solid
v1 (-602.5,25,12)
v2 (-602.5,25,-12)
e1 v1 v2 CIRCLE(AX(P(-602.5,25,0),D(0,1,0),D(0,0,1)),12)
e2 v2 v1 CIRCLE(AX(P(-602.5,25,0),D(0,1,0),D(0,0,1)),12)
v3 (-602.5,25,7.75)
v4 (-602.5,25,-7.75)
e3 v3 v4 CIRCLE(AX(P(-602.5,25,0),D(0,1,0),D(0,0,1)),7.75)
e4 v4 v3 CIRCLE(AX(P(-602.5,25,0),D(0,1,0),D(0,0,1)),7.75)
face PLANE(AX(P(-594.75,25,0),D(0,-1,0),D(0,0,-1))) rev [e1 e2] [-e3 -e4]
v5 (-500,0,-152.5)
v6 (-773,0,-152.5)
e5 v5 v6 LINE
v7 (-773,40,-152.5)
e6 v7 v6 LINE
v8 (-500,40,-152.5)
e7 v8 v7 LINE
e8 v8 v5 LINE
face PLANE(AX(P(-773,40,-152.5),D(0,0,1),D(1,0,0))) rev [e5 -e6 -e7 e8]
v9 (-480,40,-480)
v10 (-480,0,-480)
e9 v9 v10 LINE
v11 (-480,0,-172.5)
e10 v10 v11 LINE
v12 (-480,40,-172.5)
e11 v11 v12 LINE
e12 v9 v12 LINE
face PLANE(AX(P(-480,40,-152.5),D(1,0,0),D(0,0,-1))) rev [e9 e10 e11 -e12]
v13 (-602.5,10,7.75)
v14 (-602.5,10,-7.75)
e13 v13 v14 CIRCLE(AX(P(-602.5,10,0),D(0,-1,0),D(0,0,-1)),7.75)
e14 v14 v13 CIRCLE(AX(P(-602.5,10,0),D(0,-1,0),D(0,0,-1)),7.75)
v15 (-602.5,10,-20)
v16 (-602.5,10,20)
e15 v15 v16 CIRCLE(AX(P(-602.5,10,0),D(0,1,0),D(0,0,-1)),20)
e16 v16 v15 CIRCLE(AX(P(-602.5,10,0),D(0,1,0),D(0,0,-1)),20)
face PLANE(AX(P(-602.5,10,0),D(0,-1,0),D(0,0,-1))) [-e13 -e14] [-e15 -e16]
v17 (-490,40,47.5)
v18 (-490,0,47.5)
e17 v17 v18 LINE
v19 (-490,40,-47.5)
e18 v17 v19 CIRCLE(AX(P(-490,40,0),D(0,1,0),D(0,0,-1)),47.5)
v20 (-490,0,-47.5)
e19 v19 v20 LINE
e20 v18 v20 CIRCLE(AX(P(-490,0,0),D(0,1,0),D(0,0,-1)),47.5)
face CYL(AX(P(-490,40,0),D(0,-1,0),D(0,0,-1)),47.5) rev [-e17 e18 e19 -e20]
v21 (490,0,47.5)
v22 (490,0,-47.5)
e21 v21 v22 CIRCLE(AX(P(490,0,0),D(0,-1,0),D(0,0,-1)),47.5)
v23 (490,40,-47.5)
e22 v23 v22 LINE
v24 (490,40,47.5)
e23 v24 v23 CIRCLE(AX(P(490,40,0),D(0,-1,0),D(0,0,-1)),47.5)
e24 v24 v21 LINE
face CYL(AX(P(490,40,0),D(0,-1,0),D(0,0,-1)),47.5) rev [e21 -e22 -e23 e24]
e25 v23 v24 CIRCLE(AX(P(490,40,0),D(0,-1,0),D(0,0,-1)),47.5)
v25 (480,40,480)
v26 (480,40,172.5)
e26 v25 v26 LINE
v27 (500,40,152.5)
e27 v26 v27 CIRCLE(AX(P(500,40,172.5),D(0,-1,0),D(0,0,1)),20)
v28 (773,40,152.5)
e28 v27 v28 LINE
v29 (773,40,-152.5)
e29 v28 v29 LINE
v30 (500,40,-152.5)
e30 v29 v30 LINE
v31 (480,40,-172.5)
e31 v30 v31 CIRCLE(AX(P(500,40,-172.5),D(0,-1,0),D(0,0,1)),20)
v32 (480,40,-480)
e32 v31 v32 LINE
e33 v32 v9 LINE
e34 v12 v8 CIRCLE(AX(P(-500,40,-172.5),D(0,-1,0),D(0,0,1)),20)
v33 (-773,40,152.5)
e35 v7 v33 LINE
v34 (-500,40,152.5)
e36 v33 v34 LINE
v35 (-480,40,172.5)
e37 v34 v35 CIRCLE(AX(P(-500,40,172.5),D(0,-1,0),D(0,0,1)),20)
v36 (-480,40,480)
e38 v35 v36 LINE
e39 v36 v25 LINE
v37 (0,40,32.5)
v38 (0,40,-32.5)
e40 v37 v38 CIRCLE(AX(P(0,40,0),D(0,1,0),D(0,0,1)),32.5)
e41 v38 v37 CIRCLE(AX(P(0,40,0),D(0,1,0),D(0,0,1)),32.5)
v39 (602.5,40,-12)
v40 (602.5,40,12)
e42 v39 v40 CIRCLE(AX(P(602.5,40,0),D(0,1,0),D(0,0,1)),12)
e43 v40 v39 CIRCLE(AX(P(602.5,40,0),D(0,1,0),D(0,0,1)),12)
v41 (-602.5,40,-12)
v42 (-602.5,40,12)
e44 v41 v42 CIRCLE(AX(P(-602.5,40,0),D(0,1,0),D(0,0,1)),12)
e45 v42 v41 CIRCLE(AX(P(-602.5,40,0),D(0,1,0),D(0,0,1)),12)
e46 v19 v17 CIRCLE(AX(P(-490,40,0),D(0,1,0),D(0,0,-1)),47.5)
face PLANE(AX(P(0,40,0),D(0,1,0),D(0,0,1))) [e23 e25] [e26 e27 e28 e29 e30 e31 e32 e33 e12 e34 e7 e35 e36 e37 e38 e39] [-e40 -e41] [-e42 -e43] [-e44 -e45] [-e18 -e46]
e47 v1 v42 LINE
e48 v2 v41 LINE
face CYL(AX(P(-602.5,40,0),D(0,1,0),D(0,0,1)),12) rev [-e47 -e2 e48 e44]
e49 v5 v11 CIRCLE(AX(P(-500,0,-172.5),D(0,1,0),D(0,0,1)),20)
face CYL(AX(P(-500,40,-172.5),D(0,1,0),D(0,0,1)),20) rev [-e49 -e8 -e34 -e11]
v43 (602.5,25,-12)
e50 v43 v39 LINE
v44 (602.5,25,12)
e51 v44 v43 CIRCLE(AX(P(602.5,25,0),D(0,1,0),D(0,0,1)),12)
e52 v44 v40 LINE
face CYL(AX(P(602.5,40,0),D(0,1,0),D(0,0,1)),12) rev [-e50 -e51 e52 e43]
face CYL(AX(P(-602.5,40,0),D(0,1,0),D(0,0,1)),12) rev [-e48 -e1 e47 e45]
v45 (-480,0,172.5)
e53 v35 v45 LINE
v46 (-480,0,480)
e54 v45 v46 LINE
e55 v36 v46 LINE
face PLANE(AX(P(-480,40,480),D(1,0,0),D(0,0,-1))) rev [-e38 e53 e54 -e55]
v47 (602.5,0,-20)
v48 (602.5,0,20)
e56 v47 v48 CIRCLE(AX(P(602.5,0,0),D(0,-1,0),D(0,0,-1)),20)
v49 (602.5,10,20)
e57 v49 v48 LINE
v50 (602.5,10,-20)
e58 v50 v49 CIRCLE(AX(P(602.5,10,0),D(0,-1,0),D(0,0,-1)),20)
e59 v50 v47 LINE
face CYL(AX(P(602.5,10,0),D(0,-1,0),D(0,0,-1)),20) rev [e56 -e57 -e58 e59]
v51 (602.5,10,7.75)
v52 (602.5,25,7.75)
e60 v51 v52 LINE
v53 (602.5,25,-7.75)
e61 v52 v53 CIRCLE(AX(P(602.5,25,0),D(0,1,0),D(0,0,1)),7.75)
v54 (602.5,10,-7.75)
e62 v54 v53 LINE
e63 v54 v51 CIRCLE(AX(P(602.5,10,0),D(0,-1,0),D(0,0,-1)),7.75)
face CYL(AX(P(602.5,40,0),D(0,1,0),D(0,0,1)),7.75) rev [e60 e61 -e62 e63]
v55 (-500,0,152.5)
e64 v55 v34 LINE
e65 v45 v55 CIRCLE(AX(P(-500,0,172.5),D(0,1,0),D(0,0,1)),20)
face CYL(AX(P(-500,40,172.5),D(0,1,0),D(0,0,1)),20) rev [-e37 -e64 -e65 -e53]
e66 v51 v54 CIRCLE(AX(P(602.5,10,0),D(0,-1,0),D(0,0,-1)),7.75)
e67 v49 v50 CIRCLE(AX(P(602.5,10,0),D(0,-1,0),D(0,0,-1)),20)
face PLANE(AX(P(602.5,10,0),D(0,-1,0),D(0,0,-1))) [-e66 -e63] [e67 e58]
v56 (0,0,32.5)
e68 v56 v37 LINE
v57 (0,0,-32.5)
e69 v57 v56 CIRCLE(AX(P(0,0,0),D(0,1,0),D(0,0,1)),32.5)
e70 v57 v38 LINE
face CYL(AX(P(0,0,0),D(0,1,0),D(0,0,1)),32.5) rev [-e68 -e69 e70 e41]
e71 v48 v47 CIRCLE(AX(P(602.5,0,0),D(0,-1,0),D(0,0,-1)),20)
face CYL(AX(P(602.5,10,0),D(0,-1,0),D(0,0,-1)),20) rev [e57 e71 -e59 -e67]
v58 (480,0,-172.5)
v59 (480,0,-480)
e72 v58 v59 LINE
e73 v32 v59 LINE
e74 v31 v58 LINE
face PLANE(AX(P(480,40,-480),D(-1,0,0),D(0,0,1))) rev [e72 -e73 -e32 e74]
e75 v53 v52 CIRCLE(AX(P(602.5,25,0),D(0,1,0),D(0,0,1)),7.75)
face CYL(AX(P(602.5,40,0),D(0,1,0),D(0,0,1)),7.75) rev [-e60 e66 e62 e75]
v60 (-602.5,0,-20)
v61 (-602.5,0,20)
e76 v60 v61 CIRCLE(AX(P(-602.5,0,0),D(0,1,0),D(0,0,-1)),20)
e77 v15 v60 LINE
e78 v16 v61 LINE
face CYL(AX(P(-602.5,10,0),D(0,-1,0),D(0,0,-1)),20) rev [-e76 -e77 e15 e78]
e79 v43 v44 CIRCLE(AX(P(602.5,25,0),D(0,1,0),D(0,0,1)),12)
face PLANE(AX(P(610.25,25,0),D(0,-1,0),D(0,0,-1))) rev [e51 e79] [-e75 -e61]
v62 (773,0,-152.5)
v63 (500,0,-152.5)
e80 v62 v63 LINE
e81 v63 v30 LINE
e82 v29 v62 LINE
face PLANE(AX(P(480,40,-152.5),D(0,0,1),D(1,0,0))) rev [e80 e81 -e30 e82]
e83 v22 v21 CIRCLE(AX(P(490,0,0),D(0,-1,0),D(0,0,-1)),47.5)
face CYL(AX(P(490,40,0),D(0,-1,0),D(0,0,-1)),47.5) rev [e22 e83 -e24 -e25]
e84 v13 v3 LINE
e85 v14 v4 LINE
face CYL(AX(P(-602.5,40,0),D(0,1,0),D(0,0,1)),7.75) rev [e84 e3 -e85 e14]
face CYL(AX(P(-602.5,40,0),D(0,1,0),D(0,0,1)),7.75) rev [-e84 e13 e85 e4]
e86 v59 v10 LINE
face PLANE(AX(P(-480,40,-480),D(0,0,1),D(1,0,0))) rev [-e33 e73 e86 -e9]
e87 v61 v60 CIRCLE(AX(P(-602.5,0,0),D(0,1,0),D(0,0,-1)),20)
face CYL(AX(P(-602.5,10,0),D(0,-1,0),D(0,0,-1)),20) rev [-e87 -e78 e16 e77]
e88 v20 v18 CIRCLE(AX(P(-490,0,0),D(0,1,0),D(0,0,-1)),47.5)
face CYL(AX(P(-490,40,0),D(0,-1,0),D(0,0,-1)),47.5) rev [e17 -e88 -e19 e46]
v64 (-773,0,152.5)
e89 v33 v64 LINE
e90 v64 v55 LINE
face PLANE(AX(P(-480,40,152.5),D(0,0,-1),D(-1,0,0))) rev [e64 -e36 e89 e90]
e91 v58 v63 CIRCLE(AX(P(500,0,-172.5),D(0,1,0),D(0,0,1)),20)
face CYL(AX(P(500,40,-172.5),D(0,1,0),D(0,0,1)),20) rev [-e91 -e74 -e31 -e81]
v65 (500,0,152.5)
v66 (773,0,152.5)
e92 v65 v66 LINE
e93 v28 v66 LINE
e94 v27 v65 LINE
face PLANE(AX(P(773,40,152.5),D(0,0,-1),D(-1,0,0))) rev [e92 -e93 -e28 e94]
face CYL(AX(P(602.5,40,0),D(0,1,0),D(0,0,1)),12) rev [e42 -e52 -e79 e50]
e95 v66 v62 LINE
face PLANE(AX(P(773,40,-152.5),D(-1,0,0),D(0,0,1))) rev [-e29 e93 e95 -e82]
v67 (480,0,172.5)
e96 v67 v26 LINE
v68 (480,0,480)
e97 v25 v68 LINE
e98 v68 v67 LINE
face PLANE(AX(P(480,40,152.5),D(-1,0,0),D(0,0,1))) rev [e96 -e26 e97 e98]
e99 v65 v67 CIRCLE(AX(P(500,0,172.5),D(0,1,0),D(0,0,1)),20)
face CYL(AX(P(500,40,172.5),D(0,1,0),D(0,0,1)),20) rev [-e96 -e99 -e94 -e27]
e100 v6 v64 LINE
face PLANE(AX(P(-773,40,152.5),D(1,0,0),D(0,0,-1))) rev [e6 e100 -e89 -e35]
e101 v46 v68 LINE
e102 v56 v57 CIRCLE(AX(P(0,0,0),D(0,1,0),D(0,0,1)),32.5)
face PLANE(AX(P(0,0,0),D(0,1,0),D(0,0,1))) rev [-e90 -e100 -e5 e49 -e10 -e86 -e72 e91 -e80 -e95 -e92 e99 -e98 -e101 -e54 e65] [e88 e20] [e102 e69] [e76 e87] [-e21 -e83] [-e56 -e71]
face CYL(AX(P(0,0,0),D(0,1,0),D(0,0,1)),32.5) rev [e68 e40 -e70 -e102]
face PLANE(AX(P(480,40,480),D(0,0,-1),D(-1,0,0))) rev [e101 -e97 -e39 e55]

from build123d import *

# Parameters (mm, degrees)
EXTRUDE_1_DEPTH           = 40
SKETCH_2_R                = 20
CUT_EXTRUDE_1_DEPTH       = 10
HOLE_WIZARD_0_D           = 15.5
HOLE_WIZARD_0_CBORE_D     = 24
HOLE_WIZARD_0_CBORE_DEPTH = 15
SKETCH_5_R                = 47.5
CUT_EXTRUDE_2_DEPTH       = 911.7848264
SKETCH_6_R                = 32.5
CUT_EXTRUDE_3_DEPTH       = 911.7848264
FILLET_1_R                = 20


with BuildPart() as part:
    # 草图1 → 凸台-拉伸1 (new body)
    with BuildSketch(Plane(origin=(0, 0, 0), x_dir=(1, 0, 0), z_dir=(0, 1, 0))):
        Polygon((-480, 480), (480, 480), (480, 152.5), (773, 152.5), (773, -152.5), (480, -152.5), (480, -480), (-480, -480), (-480, -152.5), (-773, -152.5), (-773, 152.5), (-480, 152.5), align=None)
    extrude(amount=EXTRUDE_1_DEPTH)

    # 草图2 → 切除-拉伸1 (cut)
    with BuildSketch(Plane.XZ):
        with Locations(Location((602.5, 0, 0), (0, 0, 270))):
            Circle(SKETCH_2_R)
    cut_extrude_1 = extrude(amount=-CUT_EXTRUDE_1_DEPTH, mode=Mode.SUBTRACT)

    # 打孔尺寸(%根据)内六角圆柱头螺钉的类型0 (through all)
    with Locations(Plane(origin=(0, 40, 0), x_dir=(1, 0, 0), z_dir=(0, 1, 0))):
        with Locations((602.5, 0)):
            hole_wizard_0 = CounterBoreHole(HOLE_WIZARD_0_D / 2, HOLE_WIZARD_0_CBORE_D / 2, HOLE_WIZARD_0_CBORE_DEPTH)

    # 镜向1: 切除-拉伸1, 打孔尺寸(%根据)内六角圆柱头螺钉的类型0 across plane
    add(cut_extrude_1.mirror(Plane(origin=(0, 0, 0), x_dir=(0, 0, 1), z_dir=(1, 0, 0))), mode=Mode.SUBTRACT)
    add(hole_wizard_0.mirror(Plane(origin=(0, 0, 0), x_dir=(0, 0, 1), z_dir=(1, 0, 0))), mode=Mode.SUBTRACT)

    # 草图5 → 切除-拉伸2 (cut, through all)
    with BuildSketch(Plane.XZ):
        with Locations(Location((490, 0, 0), (0, 0, 270))):
            Circle(SKETCH_5_R)
    cut_extrude_2 = extrude(amount=-CUT_EXTRUDE_2_DEPTH, mode=Mode.SUBTRACT)

    # 镜向2: 切除-拉伸2 across plane
    add(cut_extrude_2.mirror(Plane(origin=(0, 0, 0), x_dir=(0, 0, 1), z_dir=(1, 0, 0))), mode=Mode.SUBTRACT)

    # 草图6 → 切除-拉伸3 (cut, through all)
    with BuildSketch(Plane(origin=(0, 40, 0), x_dir=(1, 0, 0), z_dir=(0, 1, 0))):
        with Locations(Location((0, 0, 0), (0, 0, 270))):
            Circle(SKETCH_6_R)
    extrude(amount=-CUT_EXTRUDE_3_DEPTH, mode=Mode.SUBTRACT)

    # 圆角1
    fillet_1_edges = [part.edges().sort_by_distance(p)[0] for p in [
        (-480, 20, 152.5),
        (-480, 20, -152.5),
        (480, 20, -152.5),
        (480, 20, 152.5),
    ]]
    fillet(fillet_1_edges, radius=FILLET_1_R)


solid = part.part
